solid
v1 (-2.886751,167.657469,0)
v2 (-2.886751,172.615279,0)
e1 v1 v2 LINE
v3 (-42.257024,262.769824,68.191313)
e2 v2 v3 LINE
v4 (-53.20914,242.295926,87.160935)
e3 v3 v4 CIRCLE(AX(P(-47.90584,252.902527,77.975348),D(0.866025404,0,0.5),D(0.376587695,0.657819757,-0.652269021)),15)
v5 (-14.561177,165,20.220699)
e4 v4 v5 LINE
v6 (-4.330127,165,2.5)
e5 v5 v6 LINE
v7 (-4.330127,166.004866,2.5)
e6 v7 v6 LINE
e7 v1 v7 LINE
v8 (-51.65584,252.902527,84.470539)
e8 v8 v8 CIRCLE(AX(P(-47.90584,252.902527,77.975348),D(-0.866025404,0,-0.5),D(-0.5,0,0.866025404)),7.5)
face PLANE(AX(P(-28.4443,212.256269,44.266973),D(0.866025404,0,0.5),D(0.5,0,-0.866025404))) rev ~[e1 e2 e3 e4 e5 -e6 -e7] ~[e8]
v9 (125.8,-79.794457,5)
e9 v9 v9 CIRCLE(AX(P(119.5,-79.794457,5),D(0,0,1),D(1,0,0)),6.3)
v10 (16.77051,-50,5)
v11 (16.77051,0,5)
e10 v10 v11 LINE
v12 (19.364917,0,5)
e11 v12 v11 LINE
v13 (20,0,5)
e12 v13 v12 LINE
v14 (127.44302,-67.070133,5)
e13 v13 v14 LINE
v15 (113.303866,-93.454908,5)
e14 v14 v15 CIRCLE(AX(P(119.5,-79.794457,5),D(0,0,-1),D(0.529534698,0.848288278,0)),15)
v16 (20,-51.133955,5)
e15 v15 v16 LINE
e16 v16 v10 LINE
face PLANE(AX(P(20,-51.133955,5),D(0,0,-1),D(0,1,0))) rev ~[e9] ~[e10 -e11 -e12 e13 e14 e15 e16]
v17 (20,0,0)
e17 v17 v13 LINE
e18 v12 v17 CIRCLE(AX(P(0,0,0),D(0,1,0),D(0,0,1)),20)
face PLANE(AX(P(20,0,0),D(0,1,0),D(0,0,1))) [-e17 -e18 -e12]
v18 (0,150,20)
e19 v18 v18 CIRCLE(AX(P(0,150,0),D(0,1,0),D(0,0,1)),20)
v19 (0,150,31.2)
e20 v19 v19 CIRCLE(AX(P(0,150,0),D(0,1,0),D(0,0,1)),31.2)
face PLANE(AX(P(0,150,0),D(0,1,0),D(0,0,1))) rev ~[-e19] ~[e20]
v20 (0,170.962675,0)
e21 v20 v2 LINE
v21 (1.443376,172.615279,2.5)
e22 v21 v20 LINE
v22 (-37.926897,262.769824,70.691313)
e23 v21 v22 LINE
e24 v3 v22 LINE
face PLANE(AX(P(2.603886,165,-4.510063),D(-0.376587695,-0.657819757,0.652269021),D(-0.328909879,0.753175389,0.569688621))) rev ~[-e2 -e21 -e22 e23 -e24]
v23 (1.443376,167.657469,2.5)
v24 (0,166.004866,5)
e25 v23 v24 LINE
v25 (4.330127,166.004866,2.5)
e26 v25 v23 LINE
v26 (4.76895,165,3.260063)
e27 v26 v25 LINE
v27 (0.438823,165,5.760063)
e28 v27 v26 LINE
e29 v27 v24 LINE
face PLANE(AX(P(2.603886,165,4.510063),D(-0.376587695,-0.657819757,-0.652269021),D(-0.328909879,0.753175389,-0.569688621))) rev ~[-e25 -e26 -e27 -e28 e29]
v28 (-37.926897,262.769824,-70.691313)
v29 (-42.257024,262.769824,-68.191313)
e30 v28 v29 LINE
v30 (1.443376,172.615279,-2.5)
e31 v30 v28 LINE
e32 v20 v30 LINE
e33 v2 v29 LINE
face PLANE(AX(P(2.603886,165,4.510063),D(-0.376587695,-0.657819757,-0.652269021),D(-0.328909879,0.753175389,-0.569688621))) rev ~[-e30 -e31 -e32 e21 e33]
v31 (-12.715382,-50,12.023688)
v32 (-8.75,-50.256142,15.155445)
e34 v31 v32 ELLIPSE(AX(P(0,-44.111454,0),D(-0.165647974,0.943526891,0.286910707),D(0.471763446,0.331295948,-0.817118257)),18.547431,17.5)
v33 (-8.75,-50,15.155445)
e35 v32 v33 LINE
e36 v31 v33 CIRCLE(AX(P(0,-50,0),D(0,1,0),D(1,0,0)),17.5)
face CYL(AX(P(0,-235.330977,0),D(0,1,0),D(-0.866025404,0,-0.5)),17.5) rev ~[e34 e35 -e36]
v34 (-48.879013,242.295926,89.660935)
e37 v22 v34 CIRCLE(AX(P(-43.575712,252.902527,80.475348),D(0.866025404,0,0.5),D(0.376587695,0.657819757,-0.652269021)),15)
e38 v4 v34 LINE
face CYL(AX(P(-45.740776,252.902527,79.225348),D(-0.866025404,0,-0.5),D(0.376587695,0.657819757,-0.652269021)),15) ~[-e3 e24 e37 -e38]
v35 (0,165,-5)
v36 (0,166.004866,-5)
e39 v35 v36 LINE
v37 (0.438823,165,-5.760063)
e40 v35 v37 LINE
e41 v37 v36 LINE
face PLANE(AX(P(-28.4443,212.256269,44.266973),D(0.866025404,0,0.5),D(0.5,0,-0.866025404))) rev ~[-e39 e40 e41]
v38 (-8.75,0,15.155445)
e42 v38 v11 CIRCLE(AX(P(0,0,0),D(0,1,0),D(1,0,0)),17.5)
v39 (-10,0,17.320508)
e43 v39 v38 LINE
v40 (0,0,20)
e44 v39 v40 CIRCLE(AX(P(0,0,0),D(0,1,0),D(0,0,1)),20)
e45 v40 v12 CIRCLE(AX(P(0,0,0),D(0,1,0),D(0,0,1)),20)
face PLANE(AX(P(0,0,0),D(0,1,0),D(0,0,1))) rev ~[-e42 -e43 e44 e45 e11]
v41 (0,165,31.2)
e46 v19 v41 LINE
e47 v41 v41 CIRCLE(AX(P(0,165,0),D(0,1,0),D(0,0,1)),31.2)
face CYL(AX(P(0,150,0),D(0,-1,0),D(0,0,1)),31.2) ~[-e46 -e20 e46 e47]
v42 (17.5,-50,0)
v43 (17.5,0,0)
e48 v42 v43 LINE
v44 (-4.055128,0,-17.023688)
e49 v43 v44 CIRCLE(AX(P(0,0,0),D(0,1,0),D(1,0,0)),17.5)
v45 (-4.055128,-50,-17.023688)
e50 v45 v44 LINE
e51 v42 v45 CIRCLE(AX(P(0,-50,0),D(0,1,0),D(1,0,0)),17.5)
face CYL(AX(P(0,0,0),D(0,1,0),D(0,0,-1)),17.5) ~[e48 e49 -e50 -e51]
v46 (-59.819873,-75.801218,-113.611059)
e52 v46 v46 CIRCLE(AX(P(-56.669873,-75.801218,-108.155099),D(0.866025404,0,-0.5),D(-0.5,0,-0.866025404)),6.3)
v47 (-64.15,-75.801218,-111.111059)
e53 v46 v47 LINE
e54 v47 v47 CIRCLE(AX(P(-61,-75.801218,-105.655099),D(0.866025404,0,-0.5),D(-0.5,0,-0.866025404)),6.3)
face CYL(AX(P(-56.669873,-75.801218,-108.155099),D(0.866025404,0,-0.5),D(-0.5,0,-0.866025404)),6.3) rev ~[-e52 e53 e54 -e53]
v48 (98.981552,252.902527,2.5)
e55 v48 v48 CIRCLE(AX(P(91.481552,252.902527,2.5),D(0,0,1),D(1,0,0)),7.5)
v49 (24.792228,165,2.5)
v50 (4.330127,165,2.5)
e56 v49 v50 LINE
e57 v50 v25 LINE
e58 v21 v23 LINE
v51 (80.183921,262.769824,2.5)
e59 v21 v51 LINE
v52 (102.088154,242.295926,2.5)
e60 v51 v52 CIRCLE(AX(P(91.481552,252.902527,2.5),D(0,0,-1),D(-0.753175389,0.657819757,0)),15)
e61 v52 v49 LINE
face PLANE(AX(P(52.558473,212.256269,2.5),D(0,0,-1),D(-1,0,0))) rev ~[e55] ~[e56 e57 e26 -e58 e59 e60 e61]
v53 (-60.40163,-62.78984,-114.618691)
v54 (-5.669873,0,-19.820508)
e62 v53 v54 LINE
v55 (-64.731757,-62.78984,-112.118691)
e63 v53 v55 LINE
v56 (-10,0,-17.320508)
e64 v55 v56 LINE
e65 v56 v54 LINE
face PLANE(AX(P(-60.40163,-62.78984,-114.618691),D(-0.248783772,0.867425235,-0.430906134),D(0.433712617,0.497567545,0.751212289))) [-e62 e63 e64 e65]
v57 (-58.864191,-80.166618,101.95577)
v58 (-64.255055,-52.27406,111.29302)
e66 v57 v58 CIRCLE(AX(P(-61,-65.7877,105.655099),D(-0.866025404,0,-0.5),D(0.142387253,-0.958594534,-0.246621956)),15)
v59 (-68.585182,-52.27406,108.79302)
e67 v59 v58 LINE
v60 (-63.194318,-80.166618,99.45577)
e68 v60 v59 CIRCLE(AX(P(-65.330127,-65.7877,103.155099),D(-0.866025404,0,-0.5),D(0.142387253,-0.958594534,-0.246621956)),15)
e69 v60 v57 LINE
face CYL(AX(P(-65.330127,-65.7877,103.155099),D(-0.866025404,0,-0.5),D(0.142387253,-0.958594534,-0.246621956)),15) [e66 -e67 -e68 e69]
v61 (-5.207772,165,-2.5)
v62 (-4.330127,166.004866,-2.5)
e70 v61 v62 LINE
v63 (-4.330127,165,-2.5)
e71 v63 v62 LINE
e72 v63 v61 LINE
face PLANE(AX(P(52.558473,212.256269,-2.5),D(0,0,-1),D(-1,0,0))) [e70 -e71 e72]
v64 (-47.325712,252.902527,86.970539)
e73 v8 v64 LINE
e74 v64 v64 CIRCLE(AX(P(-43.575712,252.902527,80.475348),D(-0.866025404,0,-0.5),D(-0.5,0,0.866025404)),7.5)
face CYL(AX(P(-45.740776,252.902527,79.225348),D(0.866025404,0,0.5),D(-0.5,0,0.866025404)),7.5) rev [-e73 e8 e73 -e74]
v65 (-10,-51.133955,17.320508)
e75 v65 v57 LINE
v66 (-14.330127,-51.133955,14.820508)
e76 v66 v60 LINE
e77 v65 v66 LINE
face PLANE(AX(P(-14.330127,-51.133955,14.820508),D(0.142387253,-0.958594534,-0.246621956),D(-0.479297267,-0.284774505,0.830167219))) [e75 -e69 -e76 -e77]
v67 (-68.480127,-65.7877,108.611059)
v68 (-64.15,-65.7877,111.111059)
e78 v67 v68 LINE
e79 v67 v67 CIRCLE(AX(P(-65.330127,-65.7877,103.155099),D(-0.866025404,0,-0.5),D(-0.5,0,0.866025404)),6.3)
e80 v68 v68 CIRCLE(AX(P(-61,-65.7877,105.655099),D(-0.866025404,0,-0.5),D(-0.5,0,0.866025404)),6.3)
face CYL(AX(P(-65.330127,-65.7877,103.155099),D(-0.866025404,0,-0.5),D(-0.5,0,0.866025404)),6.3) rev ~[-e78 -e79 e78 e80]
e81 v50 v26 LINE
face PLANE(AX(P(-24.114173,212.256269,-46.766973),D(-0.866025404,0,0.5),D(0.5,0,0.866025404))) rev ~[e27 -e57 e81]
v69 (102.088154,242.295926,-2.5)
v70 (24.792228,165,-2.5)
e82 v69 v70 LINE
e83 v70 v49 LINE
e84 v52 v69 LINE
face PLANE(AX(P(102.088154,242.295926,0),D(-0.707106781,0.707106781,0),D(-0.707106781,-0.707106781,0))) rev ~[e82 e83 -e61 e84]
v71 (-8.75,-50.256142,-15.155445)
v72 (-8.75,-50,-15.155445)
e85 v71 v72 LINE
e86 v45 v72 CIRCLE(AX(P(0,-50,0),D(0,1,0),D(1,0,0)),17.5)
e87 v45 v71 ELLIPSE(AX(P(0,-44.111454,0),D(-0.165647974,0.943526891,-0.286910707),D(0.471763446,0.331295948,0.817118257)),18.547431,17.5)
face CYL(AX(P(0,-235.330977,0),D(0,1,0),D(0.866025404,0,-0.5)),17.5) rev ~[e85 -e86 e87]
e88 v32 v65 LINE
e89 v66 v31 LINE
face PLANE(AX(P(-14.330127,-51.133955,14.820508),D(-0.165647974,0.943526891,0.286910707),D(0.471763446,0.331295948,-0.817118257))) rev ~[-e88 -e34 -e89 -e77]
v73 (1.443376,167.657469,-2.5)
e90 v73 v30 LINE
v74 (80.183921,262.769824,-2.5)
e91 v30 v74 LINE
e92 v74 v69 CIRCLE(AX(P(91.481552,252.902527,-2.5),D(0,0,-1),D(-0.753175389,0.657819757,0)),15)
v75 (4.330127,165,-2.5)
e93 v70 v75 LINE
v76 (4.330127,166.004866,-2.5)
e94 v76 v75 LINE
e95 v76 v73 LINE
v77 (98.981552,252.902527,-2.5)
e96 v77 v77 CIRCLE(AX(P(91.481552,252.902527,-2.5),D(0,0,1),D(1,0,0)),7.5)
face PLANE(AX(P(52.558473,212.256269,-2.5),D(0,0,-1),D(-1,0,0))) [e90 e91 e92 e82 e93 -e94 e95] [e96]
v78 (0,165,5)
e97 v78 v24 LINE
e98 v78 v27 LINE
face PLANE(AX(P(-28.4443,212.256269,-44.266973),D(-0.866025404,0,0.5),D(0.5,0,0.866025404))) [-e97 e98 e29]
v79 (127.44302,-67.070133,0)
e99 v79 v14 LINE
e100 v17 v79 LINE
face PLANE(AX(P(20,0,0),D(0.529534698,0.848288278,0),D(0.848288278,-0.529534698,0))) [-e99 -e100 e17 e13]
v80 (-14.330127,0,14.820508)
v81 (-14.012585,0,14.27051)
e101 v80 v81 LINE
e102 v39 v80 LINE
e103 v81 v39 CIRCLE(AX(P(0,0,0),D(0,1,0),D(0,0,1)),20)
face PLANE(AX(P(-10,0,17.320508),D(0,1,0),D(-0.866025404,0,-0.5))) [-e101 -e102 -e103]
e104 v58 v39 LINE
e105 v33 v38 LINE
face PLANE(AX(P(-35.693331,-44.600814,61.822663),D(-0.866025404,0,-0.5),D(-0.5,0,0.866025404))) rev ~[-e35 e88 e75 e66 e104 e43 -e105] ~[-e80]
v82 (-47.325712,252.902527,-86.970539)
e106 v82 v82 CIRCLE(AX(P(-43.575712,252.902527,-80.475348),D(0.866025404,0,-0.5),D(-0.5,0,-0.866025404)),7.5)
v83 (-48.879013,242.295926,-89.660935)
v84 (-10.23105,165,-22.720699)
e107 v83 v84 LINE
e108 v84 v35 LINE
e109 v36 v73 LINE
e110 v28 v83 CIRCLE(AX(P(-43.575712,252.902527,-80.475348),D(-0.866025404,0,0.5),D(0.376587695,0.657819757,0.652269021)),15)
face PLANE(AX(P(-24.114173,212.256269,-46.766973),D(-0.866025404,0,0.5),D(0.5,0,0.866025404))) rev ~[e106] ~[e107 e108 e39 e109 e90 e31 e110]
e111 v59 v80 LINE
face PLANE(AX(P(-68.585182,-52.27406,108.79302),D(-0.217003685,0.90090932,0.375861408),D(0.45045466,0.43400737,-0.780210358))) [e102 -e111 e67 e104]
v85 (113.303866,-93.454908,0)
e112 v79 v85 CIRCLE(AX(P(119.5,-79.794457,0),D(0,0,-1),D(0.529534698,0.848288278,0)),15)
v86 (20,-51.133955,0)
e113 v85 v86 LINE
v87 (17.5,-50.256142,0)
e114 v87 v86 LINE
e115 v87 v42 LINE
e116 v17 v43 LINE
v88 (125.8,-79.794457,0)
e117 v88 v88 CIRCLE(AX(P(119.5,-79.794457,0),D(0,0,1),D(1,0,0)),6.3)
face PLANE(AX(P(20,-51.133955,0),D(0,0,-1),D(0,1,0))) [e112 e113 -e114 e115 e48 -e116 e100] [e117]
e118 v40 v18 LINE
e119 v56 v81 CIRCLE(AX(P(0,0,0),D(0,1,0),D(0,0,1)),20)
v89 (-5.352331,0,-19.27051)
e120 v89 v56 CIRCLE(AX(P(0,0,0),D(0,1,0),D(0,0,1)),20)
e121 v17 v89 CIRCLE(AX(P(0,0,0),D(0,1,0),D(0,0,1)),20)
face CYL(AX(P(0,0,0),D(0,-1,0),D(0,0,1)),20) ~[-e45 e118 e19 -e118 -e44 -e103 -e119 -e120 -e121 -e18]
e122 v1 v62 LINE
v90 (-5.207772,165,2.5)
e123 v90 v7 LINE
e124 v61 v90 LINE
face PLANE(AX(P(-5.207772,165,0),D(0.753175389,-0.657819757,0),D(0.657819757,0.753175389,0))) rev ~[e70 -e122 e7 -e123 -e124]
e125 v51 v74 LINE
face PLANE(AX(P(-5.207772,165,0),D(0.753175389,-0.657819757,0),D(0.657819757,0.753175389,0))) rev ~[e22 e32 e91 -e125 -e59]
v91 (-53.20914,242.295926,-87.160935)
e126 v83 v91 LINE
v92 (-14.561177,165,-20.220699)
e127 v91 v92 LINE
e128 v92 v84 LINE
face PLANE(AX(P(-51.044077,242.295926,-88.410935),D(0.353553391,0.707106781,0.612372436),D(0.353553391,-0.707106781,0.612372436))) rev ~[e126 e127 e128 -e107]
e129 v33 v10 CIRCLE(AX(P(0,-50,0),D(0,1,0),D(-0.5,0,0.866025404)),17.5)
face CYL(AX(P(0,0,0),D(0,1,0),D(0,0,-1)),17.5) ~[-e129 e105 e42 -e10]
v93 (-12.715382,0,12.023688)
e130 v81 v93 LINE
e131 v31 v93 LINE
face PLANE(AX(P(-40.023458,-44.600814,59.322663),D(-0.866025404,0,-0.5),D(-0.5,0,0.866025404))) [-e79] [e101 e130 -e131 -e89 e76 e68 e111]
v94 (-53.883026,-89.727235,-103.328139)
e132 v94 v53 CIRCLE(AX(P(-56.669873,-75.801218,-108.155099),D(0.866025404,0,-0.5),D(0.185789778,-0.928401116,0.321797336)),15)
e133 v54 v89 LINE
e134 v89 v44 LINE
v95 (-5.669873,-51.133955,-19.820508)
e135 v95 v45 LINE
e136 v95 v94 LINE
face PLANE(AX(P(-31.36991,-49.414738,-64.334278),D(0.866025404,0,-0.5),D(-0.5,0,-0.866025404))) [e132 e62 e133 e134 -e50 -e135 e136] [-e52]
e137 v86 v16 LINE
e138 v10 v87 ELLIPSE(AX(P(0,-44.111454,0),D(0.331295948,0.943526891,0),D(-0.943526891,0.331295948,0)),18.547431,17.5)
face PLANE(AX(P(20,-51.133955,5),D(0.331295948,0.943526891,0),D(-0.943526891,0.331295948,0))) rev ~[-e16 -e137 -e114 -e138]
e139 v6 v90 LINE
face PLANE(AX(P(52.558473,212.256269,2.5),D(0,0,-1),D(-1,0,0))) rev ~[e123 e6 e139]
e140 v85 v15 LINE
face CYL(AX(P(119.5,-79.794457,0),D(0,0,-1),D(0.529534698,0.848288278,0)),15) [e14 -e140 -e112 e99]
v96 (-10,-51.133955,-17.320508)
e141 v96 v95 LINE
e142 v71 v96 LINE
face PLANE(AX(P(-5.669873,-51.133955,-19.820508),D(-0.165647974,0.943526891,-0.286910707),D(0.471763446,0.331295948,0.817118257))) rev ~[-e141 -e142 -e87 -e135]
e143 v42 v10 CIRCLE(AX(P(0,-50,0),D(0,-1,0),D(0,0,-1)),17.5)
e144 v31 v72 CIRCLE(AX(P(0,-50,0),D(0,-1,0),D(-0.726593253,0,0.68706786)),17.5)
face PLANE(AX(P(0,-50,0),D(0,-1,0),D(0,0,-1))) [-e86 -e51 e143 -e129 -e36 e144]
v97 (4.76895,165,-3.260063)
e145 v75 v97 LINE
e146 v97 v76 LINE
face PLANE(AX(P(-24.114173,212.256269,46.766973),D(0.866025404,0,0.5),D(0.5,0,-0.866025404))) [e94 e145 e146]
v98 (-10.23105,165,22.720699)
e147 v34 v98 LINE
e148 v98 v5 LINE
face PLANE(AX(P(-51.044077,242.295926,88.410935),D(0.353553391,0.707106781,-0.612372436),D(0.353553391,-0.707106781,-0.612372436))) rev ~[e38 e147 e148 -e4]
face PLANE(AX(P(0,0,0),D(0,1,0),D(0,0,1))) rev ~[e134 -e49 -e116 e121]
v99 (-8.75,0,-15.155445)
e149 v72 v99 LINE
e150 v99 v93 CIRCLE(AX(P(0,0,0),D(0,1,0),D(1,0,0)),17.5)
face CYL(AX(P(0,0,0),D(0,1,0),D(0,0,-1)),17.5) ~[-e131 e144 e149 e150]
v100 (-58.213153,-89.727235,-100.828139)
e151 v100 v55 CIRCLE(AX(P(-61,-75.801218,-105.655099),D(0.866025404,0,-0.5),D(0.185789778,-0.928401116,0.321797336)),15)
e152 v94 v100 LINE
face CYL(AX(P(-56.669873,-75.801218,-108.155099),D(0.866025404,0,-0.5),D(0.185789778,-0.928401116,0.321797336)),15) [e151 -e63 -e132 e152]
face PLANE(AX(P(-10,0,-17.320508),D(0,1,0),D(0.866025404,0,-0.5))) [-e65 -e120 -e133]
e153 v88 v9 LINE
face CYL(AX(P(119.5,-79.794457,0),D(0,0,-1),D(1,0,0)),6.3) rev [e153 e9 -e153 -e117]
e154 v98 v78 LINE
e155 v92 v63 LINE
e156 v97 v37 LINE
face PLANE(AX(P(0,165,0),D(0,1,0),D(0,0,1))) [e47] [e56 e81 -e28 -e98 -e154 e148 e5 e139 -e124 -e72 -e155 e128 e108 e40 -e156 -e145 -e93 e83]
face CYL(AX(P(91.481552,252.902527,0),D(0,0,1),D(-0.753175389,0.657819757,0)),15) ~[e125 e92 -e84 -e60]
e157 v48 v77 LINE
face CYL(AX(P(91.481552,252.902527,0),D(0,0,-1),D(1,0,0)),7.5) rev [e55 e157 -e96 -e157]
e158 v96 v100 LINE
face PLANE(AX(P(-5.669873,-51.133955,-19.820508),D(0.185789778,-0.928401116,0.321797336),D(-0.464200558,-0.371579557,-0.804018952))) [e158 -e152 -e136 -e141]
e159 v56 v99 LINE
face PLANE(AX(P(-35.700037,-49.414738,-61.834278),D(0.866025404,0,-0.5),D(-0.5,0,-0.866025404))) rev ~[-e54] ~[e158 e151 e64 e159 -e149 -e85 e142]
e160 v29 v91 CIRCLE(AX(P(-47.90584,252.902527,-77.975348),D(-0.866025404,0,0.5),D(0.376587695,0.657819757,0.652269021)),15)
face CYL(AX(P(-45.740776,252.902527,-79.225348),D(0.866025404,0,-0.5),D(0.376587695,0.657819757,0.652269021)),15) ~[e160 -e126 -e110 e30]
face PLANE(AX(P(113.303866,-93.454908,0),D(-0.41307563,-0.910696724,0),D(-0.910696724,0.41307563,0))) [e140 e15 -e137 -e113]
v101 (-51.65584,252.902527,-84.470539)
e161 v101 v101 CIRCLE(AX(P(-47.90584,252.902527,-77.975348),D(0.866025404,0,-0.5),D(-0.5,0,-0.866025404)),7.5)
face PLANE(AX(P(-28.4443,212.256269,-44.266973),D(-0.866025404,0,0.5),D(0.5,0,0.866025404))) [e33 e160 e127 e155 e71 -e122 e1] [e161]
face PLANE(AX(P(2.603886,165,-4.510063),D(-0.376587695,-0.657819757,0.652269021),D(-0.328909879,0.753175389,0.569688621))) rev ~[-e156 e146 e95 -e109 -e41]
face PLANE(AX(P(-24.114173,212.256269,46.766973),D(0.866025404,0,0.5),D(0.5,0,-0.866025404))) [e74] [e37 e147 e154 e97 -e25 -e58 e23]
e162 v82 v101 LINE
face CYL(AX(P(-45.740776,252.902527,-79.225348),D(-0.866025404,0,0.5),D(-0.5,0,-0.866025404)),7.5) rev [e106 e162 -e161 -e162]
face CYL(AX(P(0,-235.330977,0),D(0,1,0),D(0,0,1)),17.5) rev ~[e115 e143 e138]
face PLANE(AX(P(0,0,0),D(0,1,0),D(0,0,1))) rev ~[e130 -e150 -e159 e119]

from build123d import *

# Parameters (mm, degrees)
COLUMN_SKETCH_R           = 20
COLUMN_40_DEPTH           = 150
COLUMN_EXTENSION_SKETCH_R = 17.5
COLUMN_EXTENSION_35_DEPTH = 50
LEG_PLATE_SKETCH_R        = 6.3
LEG_PLATE_DEPTH           = 5
LEG_WEB_REACH             = 191.764
LEG_WEB_END_RADIUS        = 17.5
LEG_WEB_SKETCH_W          = 5
LEG_WEB_SKETCH_H          = 51.133954969
LEG_CUT_DEPTH             = 22
LEG_WEB_PATTERN_3X_COUNT  = 3
LEG_CUT_PATTERN_3X_COUNT  = 3
LEG_BOSS_A_SKETCH_R       = 6.3
LEG_BOSS_A_DEPTH          = 5
LEG_BOSS_B_SKETCH_R       = 6.3
LEG_BOSS_B_DEPTH          = 5
COLLAR_SKETCH_R           = 31.2
COLLAR_62_4_DEPTH         = 15
TOP_ARM_SKETCH_R          = 7.5
TOP_ARM_DEPTH             = 2.5
TOP_ARM_PATTERN_3X_COUNT  = 3


with BuildPart() as part:
    # Column Sketch → Column Ø40 (new body)
    with BuildSketch(Plane(origin=(0, 0, 0), x_dir=(1, 0, 0), z_dir=(0, 1, 0))):
        with Locations(Location((0, 0, 0), (0, 0, 270))):
            Circle(COLUMN_SKETCH_R)
    extrude(amount=COLUMN_40_DEPTH)

    # Column Extension Sketch → Column Extension Ø35 (add)
    with BuildSketch(Plane.XZ):
        with Locations(Location((0, 0, 0), (0, 0, 270))):
            Circle(COLUMN_EXTENSION_SKETCH_R)
    extrude(amount=COLUMN_EXTENSION_35_DEPTH)



with BuildPart() as body_2:
    # Leg Plate Sketch → Leg Plate (new body)
    with BuildSketch(Plane.XY):
        with BuildLine():
            Line((20, 0), (127.443020473, -67.070132718))
            ThreePointArc((127.443020473, -67.070132718), (132.721270407, -86.87951221), (113.303865545, -93.454907759))
            Line((113.303865545, -93.454907759), (20, -51.133954969))
            Line((20, -51.133954969), (20, 0))
        make_face()
        with Locations((119.5, -79.794456895)):
            Circle(LEG_PLATE_SKETCH_R, mode=Mode.SUBTRACT)
    extrude(amount=LEG_PLATE_DEPTH)


with BuildPart() as part_1:
    add(part.part)

    add(body_2.part)  # Leg Web merges body 2
    # Leg Web: up to this cylinder (the profile starts outside it)
    leg_web_end = Plane(origin=(0, -25.566977, 0), z_dir=(0, 1, 0)) * Cylinder(LEG_WEB_END_RADIUS, 419.528, mode=Mode.PRIVATE)
    # Leg Web Sketch → Leg Web (add, up to the surface)
    with BuildSketch(Plane.ZY.offset(-20), mode=Mode.PRIVATE) as leg_web_sk1:
        with Locations((2.5, -25.566977485)):
            Rectangle(LEG_WEB_SKETCH_W, LEG_WEB_SKETCH_H)
    leg_web_tool1 = extrude(leg_web_sk1.sketch, amount=LEG_WEB_REACH, mode=Mode.PRIVATE) - leg_web_end
    leg_web = leg_web_tool1.solids().sort_by_distance((20, -25.566977, 2.5))[0]
    add(leg_web)

    # Leg Cut Sketch → Leg Cut (cut)
    with BuildSketch(Plane.XY.offset(5)):
        Polygon((20, -51.133954969), (16.770509831, -50), (16.770509831, -51.133954969), align=None)
    leg_cut = extrude(amount=-LEG_CUT_DEPTH, mode=Mode.SUBTRACT)

    # Leg Web Pattern 3x: Leg Web ×3 about axis
    leg_web_pattern_3x_axis = Axis((0, 0, 0), (0, 1, 0))
    for i in range(1, LEG_WEB_PATTERN_3X_COUNT):
        add(leg_web.rotate(leg_web_pattern_3x_axis, i * 360 / LEG_WEB_PATTERN_3X_COUNT))

    # Leg Cut Pattern 3x: Leg Cut ×3 about axis
    leg_cut_pattern_3x_axis = Axis((0, 0, 0), (0, 1, 0))
    for i in range(1, LEG_CUT_PATTERN_3X_COUNT):
        add(leg_cut.rotate(leg_cut_pattern_3x_axis, i * 360 / LEG_CUT_PATTERN_3X_COUNT), mode=Mode.SUBTRACT)

    # Leg Boss A Sketch → Leg Boss A (add)
    with BuildSketch(Plane(origin=(4.330127019, 0, -2.5), x_dir=(-0.49999999999999195, 0, -0.8660254037844434), z_dir=(0.8660254037844434, 0, -0.49999999999999195))):
        with BuildLine():
            Line((20, -51.133954969), (116.426306648, -89.727235024))
            ThreePointArc((116.426306648, -89.727235024), (135.501802499, -82.335843689), (129.463513173, -62.789839753))
            Line((129.463513173, -62.789839753), (20, 0))
            Line((20, 0), (20, -51.133954969))
        make_face()
        with Locations((122, -75.801218278)):
            Circle(LEG_BOSS_A_SKETCH_R, mode=Mode.SUBTRACT)
    extrude(amount=-LEG_BOSS_A_DEPTH)

    # Leg Boss B Sketch → Leg Boss B (add)
    with BuildSketch(Plane(origin=(-4.330127019, 0, -2.5), x_dir=(-0.5000000000000041, 0, 0.8660254037844364), z_dir=(-0.8660254037844363, 0, -0.500000000000004))):
        with BuildLine():
            Line((20, -51.133954969), (117.728382424, -80.166617623))
            ThreePointArc((117.728382424, -80.166617623), (135.9911189, -71.195896344), (128.510110547, -52.274059807))
            Line((128.510110547, -52.274059807), (20, 0))
            Line((20, 0), (20, -51.133954969))
        make_face()
        with Locations((122, -65.787699608)):
            Circle(LEG_BOSS_B_SKETCH_R, mode=Mode.SUBTRACT)
    extrude(amount=-LEG_BOSS_B_DEPTH)

    # Collar Sketch → Collar Ø62.4 (add)
    with BuildSketch(Plane(origin=(0, 150, 0), x_dir=(1, 0, 0), z_dir=(0, 1, 0))):
        with Locations(Location((0, 0, 0), (0, 0, 270))):
            Circle(COLLAR_SKETCH_R)
    extrude(amount=COLLAR_62_4_DEPTH)

    # Top Arm Sketch → Top Arm (add, symmetric)
    with BuildSketch(Plane.XY):
        with BuildLine():
            Line((-5.207772038, 165), (80.183921166, 262.769823837))
            ThreePointArc((80.183921166, 262.769823837), (101.724330238, 263.860880188), (102.088153724, 242.295925762))
            Line((102.088153724, 242.295925762), (24.792227962, 165))
            Line((24.792227962, 165), (-5.207772038, 165))
        make_face()
        with Locations((91.481552006, 252.902527479)):
            Circle(TOP_ARM_SKETCH_R, mode=Mode.SUBTRACT)
    top_arm = extrude(amount=TOP_ARM_DEPTH, both=True)

    # Top Arm Pattern 3x: Top Arm ×3 about axis
    top_arm_pattern_3x_axis = Axis((0, 0, 0), (0, 1, 0))
    for i in range(1, TOP_ARM_PATTERN_3X_COUNT):
        add(top_arm.rotate(top_arm_pattern_3x_axis, i * 360 / TOP_ARM_PATTERN_3X_COUNT))


solid = part_1.part
